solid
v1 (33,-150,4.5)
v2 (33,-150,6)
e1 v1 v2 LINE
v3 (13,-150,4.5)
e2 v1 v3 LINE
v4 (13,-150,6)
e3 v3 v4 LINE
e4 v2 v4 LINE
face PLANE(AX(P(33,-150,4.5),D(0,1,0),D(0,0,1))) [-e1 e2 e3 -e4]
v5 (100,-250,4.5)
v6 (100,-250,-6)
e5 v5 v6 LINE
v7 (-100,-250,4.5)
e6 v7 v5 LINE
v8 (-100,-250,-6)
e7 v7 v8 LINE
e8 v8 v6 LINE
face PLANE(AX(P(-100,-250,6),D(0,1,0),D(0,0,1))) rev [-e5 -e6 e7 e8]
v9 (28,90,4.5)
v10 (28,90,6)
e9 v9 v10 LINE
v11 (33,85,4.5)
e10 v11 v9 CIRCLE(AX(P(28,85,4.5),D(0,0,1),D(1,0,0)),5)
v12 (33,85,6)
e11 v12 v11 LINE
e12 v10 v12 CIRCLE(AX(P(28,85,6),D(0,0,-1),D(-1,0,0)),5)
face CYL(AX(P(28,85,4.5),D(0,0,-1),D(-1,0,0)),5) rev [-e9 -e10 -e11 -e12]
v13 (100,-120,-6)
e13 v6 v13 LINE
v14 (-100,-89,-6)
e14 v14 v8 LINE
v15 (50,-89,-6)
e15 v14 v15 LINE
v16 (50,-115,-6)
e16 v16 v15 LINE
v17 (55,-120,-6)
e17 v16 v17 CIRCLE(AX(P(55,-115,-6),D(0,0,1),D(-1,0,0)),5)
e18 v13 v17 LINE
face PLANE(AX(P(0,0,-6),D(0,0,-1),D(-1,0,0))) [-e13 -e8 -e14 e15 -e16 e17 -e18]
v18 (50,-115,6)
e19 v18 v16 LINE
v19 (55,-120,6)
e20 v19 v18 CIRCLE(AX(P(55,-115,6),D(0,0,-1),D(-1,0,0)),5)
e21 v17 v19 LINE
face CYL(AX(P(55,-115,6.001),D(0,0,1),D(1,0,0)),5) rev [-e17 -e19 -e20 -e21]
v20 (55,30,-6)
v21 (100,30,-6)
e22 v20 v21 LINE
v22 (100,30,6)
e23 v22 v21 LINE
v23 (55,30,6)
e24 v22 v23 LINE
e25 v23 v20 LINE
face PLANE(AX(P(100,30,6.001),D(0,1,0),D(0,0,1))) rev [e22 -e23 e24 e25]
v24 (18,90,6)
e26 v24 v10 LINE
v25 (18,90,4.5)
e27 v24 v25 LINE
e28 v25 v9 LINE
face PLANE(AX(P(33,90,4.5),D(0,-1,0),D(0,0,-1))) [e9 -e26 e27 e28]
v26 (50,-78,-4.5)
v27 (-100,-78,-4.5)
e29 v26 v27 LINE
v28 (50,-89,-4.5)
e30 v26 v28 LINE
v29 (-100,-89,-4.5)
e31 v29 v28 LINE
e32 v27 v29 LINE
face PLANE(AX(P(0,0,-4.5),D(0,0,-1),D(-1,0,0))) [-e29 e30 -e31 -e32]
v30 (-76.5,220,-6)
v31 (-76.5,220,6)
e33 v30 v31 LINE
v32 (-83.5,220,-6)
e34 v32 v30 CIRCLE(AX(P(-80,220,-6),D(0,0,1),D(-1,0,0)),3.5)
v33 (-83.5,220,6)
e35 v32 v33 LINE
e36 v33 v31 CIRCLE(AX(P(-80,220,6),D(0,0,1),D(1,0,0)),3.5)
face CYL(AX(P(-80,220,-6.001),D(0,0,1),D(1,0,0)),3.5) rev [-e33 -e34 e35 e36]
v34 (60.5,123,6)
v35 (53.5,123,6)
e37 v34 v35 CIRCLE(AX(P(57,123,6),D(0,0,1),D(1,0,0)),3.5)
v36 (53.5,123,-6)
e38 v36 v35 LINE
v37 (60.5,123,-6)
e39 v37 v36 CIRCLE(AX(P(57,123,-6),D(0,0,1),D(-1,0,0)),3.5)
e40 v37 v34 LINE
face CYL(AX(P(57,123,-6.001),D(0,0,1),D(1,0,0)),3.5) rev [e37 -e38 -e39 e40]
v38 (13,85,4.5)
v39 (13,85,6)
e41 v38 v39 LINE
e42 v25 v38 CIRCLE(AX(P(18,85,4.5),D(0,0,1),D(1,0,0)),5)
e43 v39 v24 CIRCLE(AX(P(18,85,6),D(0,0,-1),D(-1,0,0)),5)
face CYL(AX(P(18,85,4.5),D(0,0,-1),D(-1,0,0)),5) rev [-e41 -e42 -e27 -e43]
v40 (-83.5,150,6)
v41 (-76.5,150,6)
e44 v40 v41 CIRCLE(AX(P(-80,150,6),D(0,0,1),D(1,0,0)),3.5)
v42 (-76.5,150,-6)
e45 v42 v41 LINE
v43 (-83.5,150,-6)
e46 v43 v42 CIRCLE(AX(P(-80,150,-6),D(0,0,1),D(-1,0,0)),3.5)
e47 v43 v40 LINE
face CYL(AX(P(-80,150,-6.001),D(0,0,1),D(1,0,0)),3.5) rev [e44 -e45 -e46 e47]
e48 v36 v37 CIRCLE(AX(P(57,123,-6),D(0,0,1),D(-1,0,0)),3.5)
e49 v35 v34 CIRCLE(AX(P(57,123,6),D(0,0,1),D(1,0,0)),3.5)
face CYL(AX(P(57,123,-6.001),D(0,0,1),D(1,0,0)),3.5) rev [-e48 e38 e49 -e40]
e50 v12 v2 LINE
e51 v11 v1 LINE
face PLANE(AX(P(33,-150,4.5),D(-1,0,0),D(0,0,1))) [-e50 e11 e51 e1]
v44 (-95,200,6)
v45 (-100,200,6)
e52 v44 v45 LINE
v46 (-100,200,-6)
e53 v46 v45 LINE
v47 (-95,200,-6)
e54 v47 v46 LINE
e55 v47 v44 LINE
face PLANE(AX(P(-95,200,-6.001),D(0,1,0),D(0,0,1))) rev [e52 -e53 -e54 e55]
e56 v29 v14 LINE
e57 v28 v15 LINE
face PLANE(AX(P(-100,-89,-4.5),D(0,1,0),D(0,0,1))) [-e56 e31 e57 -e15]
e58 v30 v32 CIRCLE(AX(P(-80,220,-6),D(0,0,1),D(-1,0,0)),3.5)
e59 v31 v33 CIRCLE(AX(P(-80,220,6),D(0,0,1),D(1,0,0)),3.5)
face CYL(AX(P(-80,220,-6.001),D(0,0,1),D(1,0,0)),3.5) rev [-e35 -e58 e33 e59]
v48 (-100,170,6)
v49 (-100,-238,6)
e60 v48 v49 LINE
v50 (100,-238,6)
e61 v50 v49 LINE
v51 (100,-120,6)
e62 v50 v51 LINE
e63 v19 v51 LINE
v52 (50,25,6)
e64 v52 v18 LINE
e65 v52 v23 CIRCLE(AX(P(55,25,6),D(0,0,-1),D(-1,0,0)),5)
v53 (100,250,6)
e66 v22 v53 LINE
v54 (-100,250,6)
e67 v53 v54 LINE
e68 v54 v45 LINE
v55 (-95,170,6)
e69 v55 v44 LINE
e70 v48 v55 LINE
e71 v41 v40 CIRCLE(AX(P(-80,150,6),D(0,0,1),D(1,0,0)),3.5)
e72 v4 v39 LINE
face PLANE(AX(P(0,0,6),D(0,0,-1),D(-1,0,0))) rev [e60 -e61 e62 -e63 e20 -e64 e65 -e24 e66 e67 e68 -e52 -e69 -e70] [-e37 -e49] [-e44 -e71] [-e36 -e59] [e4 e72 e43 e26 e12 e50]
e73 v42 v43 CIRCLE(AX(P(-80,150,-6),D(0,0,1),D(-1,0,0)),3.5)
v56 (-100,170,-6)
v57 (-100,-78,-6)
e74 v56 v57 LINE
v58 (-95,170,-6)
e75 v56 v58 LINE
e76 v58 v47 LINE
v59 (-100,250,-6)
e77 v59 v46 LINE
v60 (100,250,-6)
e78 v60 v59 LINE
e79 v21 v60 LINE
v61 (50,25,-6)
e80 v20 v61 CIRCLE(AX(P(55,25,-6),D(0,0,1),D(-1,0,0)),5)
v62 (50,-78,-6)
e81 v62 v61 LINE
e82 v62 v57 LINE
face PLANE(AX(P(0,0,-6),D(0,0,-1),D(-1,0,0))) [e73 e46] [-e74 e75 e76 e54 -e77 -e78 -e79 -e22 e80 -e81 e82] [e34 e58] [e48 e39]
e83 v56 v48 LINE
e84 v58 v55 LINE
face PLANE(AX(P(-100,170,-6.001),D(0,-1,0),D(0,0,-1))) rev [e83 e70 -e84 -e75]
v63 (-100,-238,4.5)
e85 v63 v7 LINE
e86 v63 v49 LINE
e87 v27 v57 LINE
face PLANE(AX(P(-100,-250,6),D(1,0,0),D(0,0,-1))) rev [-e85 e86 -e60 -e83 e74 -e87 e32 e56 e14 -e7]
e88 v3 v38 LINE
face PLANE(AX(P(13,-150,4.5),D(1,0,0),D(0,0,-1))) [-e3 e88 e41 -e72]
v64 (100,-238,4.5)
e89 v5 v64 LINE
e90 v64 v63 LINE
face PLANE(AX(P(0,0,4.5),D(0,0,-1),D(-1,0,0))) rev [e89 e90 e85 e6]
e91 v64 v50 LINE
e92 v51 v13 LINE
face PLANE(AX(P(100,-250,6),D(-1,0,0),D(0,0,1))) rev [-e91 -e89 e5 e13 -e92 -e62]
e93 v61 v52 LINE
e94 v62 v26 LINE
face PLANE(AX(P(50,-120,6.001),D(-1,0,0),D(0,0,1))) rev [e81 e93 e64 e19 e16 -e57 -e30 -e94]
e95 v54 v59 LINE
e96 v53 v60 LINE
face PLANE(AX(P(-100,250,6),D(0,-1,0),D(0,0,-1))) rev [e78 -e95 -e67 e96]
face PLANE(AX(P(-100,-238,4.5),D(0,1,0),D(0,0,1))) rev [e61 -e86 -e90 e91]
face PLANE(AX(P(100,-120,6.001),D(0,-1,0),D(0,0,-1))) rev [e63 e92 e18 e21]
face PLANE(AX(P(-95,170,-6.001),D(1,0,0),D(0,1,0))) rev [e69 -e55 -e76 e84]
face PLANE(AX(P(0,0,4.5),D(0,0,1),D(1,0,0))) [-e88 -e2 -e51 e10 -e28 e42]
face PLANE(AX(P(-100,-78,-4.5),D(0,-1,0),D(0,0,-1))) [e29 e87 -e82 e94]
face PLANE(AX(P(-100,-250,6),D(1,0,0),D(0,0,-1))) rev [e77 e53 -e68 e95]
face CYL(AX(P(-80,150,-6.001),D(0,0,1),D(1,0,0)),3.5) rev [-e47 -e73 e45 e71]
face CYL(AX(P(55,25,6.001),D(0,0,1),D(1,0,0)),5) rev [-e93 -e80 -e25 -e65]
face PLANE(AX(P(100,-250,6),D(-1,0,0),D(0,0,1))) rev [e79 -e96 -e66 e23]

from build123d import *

# Parameters (mm, degrees)
SKETCH_1_W          = 200
SKETCH_1_H          = 500
EXTRUDE_1_DEPTH     = 6
SKETCH_2_W          = 200
SKETCH_2_H          = 11
CUT_EXTRUDE_1_DEPTH = 1.5
CUT_EXTRUDE_2_REACH = 271.526
SKETCH_3_W          = 5
SKETCH_3_H          = 30
CUT_EXTRUDE_3_REACH = 271.526
SKETCH_4_R          = 3.5
SKETCH_5_W          = 20
SKETCH_5_H          = 240
CUT_EXTRUDE_4_DEPTH = 1.5
FILLET_1_R          = 5
CUT_EXTRUDE_5_REACH = 271.526
SKETCH_6_W          = 50
SKETCH_6_H          = 150
FILLET_2_R          = 5
SKETCH_7_W          = 200
SKETCH_7_H          = 12
CUT_EXTRUDE_6_DEPTH = 1.5


with BuildPart() as part:
    # 草图1 → 凸台-拉伸1 (new, symmetric)
    with BuildSketch(Plane.XY):
        Rectangle(SKETCH_1_W, SKETCH_1_H)
    extrude(amount=EXTRUDE_1_DEPTH, both=True)

    # 草图2 → 切除-拉伸1 (cut)
    with BuildSketch(Plane.XY.offset(-6)):
        with Locations((0, -83.5)):
            Rectangle(SKETCH_2_W, SKETCH_2_H)
    extrude(amount=CUT_EXTRUDE_1_DEPTH, mode=Mode.SUBTRACT)

    # 草图3 → 切除-拉伸2 (cut, up to next)
    with BuildSketch(Plane.XY.offset(6), mode=Mode.PRIVATE) as cut_extrude_2_sk1:
        with Locations((-97.5, 185)):
            Rectangle(SKETCH_3_W, SKETCH_3_H)
    cut_extrude_2_tool1 = extrude(cut_extrude_2_sk1.sketch, amount=-CUT_EXTRUDE_2_REACH, mode=Mode.PRIVATE) & part.part
    add(cut_extrude_2_tool1.solids().sort_by_distance((-97.5, 185, 6))[0], mode=Mode.SUBTRACT)

    # 草图4 → 切除-拉伸3 (cut, up to next)
    with BuildSketch(Plane.XY.offset(6), mode=Mode.PRIVATE) as cut_extrude_3_sk1:
        with Locations((-80, 220)):
            Circle(SKETCH_4_R)
    cut_extrude_3_tool1 = extrude(cut_extrude_3_sk1.sketch, amount=-CUT_EXTRUDE_3_REACH, mode=Mode.PRIVATE) & part.part
    # 草图4 → 切除-拉伸3 (cut, up to next)
    with BuildSketch(Plane.XY.offset(6), mode=Mode.PRIVATE) as cut_extrude_3_sk2:
        with Locations((-80, 150)):
            Circle(SKETCH_4_R)
    cut_extrude_3_tool2 = extrude(cut_extrude_3_sk2.sketch, amount=-CUT_EXTRUDE_3_REACH, mode=Mode.PRIVATE) & part.part
    # 草图4 → 切除-拉伸3 (cut, up to next)
    with BuildSketch(Plane.XY.offset(6), mode=Mode.PRIVATE) as cut_extrude_3_sk3:
        with Locations((57, 123)):
            Circle(SKETCH_4_R)
    cut_extrude_3_tool3 = extrude(cut_extrude_3_sk3.sketch, amount=-CUT_EXTRUDE_3_REACH, mode=Mode.PRIVATE) & part.part
    add(cut_extrude_3_tool1.solids().sort_by_distance((-80, 220, 6))[0], mode=Mode.SUBTRACT)
    add(cut_extrude_3_tool2.solids().sort_by_distance((-80, 150, 6))[0], mode=Mode.SUBTRACT)
    add(cut_extrude_3_tool3.solids().sort_by_distance((57, 123, 6))[0], mode=Mode.SUBTRACT)

    # 草图5 → 切除-拉伸4 (cut)
    with BuildSketch(Plane(origin=(0, 0, 6), x_dir=(-1, 0, 0), z_dir=(0, 0, -1))):
        with Locations((-23, -30)):
            Rectangle(SKETCH_5_W, SKETCH_5_H)
    extrude(amount=CUT_EXTRUDE_4_DEPTH, mode=Mode.SUBTRACT)

    # 圆角1
    fillet_1_edges = [part.edges().sort_by_distance(p)[0] for p in [
        (33, 90, 5.25),
        (13, 90, 5.25),
    ]]
    fillet(fillet_1_edges, radius=FILLET_1_R)

    # 草图6 → 切除-拉伸5 (cut, up to next)
    with BuildSketch(Plane(origin=(0, 0, -6), x_dir=(-1, 0, 0), z_dir=(0, 0, -1)), mode=Mode.PRIVATE) as cut_extrude_5_sk1:
        with Locations((-75, -45)):
            Rectangle(SKETCH_6_W, SKETCH_6_H)
    cut_extrude_5_tool1 = extrude(cut_extrude_5_sk1.sketch, amount=-CUT_EXTRUDE_5_REACH, mode=Mode.PRIVATE) & part.part
    add(cut_extrude_5_tool1.solids().sort_by_distance((75, -45, -6))[0], mode=Mode.SUBTRACT)

    # 圆角2
    fillet_2_edges = [part.edges().sort_by_distance(p)[0] for p in [
        (50, 30, 0),
        (50, -120, 0),
    ]]
    fillet(fillet_2_edges, radius=FILLET_2_R)

    # 草图7 → 切除-拉伸6 (cut)
    with BuildSketch(Plane.XY.offset(6)):
        with Locations((0, -244)):
            Rectangle(SKETCH_7_W, SKETCH_7_H)
    extrude(amount=-CUT_EXTRUDE_6_DEPTH, mode=Mode.SUBTRACT)


solid = part.part
